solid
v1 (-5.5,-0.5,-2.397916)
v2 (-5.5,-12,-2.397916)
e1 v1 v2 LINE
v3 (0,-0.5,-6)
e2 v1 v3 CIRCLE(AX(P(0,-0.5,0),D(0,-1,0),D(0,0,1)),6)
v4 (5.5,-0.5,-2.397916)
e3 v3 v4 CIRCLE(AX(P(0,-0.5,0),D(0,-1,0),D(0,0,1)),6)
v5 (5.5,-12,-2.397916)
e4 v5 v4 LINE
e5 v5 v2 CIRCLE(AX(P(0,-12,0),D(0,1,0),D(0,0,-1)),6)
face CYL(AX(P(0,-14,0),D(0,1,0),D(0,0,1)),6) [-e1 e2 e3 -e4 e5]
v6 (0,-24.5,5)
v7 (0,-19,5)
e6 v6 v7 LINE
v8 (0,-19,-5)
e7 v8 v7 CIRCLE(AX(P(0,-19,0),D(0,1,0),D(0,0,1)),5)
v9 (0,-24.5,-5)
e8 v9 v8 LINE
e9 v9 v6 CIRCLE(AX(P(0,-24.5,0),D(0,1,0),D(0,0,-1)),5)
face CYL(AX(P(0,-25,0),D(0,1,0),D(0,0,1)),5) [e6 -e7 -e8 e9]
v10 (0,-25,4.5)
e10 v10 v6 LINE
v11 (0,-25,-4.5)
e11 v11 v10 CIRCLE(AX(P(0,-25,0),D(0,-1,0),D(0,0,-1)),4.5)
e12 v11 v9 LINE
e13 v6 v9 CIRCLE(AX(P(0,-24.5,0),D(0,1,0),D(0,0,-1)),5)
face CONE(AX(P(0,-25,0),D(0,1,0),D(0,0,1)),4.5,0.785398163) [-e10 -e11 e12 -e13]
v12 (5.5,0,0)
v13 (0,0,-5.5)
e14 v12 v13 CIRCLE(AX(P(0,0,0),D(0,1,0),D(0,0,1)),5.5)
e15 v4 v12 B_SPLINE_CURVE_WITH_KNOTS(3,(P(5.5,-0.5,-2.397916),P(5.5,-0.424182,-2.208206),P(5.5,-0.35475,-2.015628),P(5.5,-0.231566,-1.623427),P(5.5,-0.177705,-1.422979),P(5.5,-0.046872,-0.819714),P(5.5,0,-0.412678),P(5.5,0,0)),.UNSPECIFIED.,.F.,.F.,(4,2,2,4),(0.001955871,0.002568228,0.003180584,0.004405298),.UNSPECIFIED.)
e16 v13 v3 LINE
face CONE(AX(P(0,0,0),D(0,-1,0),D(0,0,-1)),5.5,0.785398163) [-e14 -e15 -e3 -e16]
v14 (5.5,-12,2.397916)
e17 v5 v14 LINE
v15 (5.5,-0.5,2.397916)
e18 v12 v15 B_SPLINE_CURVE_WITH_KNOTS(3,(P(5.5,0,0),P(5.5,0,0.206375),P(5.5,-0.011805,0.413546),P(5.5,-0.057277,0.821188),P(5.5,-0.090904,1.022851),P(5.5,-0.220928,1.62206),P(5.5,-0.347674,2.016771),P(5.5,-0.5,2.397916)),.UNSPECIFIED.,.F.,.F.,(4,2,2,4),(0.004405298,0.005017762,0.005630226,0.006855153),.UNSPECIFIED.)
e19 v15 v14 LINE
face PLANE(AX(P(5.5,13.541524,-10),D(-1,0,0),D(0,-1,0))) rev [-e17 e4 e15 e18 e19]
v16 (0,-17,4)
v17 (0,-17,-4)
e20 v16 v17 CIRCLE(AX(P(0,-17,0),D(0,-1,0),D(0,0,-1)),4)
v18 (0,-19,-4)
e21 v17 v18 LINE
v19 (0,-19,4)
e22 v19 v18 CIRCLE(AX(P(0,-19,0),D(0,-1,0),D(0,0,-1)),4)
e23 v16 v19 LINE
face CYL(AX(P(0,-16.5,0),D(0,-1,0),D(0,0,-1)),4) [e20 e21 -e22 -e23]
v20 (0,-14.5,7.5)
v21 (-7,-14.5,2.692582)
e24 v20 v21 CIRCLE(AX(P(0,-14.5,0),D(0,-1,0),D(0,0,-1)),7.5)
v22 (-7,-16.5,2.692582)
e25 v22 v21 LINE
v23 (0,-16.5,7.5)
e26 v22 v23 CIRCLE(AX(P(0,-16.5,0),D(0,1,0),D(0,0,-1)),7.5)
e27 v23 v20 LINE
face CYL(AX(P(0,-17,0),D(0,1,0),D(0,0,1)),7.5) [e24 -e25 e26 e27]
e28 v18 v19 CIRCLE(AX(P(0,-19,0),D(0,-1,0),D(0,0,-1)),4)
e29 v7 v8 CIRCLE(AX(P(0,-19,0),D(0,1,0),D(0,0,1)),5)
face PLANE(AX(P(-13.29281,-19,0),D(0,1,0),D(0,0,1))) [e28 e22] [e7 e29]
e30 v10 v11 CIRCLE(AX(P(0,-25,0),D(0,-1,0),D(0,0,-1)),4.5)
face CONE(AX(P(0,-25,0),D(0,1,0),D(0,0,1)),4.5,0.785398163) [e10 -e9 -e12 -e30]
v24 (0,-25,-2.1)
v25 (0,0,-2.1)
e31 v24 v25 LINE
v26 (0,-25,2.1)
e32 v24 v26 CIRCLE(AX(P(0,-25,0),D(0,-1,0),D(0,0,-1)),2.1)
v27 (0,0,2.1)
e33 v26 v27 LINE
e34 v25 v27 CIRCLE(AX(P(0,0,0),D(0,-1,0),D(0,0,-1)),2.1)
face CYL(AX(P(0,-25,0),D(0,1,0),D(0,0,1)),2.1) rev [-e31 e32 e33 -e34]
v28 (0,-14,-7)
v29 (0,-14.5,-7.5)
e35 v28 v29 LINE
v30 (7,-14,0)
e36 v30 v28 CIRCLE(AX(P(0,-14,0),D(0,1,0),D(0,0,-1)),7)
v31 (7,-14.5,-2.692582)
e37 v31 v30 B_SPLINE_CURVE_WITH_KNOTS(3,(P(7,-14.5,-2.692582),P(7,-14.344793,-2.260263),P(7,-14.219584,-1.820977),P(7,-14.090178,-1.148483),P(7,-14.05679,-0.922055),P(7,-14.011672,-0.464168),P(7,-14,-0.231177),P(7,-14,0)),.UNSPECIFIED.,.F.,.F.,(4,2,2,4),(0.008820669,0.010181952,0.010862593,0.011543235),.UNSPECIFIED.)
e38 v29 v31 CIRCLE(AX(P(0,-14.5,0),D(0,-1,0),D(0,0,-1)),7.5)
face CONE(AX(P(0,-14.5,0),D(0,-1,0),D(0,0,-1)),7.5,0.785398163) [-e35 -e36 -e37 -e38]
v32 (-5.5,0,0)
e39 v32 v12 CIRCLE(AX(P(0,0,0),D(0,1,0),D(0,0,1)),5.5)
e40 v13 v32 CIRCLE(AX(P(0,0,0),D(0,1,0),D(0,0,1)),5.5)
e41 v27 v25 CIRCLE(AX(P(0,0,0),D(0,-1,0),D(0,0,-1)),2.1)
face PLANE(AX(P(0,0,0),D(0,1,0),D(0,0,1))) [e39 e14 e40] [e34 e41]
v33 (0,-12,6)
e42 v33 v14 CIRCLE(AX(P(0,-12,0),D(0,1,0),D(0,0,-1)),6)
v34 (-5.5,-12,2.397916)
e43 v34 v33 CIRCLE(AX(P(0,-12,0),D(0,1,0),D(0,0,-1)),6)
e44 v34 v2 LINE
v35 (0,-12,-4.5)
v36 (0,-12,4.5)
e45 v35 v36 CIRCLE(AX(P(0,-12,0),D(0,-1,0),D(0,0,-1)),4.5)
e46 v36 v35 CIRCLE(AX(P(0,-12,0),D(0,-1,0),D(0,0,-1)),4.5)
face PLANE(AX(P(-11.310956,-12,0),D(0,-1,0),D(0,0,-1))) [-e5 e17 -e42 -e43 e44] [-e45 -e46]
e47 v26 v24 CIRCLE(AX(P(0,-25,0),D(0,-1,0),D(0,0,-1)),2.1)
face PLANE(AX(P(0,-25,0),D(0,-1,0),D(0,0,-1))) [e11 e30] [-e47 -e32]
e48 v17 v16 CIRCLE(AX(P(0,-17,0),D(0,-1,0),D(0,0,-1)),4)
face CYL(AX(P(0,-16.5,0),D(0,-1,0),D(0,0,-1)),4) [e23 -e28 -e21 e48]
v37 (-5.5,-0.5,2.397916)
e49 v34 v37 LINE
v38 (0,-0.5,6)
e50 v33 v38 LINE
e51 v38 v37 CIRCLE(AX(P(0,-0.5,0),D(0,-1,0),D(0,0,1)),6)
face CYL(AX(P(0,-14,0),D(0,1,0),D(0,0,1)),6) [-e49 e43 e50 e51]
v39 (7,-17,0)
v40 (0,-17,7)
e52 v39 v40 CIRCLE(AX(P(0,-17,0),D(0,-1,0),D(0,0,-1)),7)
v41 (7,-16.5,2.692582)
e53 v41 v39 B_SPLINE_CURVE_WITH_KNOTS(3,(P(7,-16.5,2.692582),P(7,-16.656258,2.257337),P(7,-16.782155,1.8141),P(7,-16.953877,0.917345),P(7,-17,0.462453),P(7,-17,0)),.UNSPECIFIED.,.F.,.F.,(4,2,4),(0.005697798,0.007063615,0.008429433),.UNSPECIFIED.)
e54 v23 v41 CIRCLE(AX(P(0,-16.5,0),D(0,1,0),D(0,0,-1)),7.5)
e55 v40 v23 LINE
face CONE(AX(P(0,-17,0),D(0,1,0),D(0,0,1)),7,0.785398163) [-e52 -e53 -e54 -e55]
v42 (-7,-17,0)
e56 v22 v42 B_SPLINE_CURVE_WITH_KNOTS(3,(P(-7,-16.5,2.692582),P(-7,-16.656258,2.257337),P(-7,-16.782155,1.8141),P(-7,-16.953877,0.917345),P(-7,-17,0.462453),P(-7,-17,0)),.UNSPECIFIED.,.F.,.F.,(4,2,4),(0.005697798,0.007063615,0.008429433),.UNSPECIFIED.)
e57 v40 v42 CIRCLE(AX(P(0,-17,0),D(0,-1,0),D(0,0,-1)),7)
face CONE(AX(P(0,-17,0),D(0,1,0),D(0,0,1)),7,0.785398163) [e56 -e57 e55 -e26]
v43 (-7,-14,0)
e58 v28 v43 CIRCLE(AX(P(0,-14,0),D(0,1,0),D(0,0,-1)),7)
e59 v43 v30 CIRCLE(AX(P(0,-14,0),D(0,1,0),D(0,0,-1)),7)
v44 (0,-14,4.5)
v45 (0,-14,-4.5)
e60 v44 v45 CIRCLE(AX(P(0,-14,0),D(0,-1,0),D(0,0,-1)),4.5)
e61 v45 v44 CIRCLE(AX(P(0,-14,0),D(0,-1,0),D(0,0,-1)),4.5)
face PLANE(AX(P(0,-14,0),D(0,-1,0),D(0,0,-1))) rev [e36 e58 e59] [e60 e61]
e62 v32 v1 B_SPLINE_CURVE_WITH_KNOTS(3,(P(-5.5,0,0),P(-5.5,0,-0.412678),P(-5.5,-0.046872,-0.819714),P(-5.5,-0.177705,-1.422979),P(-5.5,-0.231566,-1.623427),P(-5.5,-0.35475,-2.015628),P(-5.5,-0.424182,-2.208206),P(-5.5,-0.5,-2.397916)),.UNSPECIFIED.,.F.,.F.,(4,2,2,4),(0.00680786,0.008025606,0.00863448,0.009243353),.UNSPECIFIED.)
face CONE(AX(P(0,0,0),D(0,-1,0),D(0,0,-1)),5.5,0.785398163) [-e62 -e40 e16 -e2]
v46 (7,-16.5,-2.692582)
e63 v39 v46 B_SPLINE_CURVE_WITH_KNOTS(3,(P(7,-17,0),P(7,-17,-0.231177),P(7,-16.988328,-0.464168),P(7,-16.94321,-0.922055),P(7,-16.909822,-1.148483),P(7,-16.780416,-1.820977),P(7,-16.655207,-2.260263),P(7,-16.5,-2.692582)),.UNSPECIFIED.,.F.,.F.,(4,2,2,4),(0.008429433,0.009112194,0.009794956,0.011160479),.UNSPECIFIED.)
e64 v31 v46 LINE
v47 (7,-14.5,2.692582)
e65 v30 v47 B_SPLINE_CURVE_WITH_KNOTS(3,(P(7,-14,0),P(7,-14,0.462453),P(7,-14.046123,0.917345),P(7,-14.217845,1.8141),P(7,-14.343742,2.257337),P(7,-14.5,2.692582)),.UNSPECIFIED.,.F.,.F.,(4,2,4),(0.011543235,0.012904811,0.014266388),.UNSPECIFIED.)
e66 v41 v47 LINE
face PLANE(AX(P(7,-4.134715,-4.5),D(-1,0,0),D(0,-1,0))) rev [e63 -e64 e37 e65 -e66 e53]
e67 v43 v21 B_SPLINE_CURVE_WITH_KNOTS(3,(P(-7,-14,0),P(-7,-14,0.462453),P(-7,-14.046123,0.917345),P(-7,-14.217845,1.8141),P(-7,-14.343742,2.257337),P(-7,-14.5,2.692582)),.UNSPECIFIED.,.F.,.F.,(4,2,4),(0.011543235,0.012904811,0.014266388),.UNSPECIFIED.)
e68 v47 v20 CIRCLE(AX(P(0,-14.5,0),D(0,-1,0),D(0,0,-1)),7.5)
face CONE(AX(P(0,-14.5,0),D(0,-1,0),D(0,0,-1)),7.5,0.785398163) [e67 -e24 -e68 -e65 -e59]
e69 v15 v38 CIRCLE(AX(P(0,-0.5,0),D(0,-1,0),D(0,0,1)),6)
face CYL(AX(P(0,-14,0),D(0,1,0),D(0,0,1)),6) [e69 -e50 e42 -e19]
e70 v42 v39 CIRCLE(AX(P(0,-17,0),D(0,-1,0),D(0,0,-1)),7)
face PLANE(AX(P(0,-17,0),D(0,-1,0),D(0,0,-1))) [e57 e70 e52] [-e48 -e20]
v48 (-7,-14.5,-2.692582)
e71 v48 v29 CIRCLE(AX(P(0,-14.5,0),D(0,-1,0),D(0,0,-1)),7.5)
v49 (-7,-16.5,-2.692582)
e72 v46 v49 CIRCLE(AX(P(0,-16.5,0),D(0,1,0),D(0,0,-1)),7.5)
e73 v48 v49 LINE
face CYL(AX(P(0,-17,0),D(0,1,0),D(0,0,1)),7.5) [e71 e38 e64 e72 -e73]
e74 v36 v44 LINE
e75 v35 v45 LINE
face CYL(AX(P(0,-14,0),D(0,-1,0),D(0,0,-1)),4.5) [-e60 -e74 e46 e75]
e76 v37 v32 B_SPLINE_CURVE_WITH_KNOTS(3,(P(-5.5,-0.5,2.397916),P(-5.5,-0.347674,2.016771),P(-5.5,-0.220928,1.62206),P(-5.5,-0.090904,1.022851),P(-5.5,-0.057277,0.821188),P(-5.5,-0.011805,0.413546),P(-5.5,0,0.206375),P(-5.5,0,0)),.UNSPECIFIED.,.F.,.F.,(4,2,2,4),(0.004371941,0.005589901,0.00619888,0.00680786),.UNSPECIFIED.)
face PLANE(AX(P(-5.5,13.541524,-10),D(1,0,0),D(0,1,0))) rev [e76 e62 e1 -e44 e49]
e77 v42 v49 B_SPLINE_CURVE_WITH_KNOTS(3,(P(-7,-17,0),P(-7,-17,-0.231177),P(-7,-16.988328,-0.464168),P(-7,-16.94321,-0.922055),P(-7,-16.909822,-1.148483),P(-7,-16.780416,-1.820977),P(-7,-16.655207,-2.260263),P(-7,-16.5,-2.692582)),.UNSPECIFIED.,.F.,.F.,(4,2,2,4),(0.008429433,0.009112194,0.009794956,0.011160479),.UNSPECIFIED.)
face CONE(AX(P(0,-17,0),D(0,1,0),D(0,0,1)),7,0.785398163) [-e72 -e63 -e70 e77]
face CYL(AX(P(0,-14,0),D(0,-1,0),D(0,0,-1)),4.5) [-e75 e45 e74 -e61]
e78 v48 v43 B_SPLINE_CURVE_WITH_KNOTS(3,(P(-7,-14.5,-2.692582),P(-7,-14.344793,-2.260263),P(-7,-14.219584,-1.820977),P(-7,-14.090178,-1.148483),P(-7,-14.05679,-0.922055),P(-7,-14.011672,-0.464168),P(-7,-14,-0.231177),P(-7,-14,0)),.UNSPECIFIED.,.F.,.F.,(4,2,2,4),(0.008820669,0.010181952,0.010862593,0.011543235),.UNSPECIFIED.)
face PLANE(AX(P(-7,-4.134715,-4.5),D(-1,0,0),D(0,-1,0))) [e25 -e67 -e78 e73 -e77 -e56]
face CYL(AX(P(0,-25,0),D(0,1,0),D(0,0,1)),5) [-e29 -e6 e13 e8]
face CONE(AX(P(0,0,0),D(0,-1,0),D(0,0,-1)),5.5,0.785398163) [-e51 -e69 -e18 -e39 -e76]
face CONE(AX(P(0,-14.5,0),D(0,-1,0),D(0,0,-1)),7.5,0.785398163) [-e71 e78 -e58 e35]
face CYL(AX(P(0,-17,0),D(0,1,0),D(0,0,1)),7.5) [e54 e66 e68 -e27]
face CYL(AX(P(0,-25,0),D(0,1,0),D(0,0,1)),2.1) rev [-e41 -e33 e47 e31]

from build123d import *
from build123d.topology import SkipClean

# Parameters (mm, degrees)
SKETCH_1_R          = 6
EXTRUDE_1_DEPTH     = 14
SKETCH_2_R          = 7.5
EXTRUDE_2_DEPTH     = 3
SKETCH_3_R          = 5
EXTRUDE_3_DEPTH     = 8
SKETCH_8_R          = 2.1
CUT_EXTRUDE_1_DEPTH = 28.156951228
CHAMFER_1_SIZE      = 0.5
SKETCH_9_W          = 14.77232069
SKETCH_9_H          = 13.551998546
CUT_EXTRUDE_2_DEPTH = 4.5
CHAMFER_2_SIZE      = 0.5
SKETCH_11_W         = 9.643873146
SKETCH_11_H         = 27.541523797
SKETCH_11_W_2       = 13.856983611
CUT_EXTRUDE_3_DEPTH = 10
SKETCH_12_W         = 9.292809808
SKETCH_12_H         = 2
SKETCH_13_W         = 6.810956272
SKETCH_13_H         = 2


with BuildPart() as part:
    # 草图1 → 凸台-拉伸1 (new body)
    with BuildSketch(Plane(origin=(0, 0, 0), x_dir=(1, 0, 0), z_dir=(0, 1, 0))):
        with Locations(Location((0, 0, 0), (0, 0, 270))):
            Circle(SKETCH_1_R)
    extrude(amount=-EXTRUDE_1_DEPTH)

    # 草图2 → 凸台-拉伸2 (add)
    with BuildSketch(Plane.XZ.offset(14)):
        with Locations(Location((0, 0, 0), (0, 0, 270))):
            Circle(SKETCH_2_R)
    extrude(amount=EXTRUDE_2_DEPTH)

    # 草图3 → 凸台-拉伸3 (add)
    with BuildSketch(Plane.XZ.offset(17)):
        with Locations(Location((0, 0, 0), (0, 0, 270))):
            Circle(SKETCH_3_R)
    extrude(amount=EXTRUDE_3_DEPTH)

    # 草图8 → 切除-拉伸1 (cut, through all)
    with BuildSketch(Plane.XZ):
        with Locations(Location((0, 0, 0), (0, 0, 270))):
            Circle(SKETCH_8_R)
    extrude(amount=CUT_EXTRUDE_1_DEPTH, mode=Mode.SUBTRACT)

    # 倒角1
    chamfer_1_edges = [part.edges().sort_by_distance(p)[0] for p in [
        (0, 0, -6),
        (0, -14, 7.5),
        (0, -17, 7.5),
    ]]
    chamfer(chamfer_1_edges, length=CHAMFER_1_SIZE)

    # 草图9 → 切除-拉伸2 (cut, symmetric)
    with SkipClean():  # the faces are left unmerged after this step: merging them gives an invalid solid
        with BuildSketch(Plane.XY):
            with Locations((14.386160345, -10.910714622)):
                Rectangle(SKETCH_9_W, SKETCH_9_H)
        cut_extrude_2 = extrude(amount=CUT_EXTRUDE_2_DEPTH, both=True, mode=Mode.SUBTRACT)

    # 镜向1: 切除-拉伸2 across plane
    add(cut_extrude_2.mirror(Plane(origin=(0, 0, 0), x_dir=(0, 0, 1), z_dir=(1, 0, 0))), mode=Mode.SUBTRACT)

    # 倒角2
    chamfer_2_edges = [part.edges().sort_by_distance(p)[0] for p in [
        (0, -25, 5),
    ]]
    chamfer(chamfer_2_edges, length=CHAMFER_2_SIZE)

    # 草图11 → 切除-拉伸3 (cut, symmetric)
    with BuildSketch(Plane.XY):
        with Locations((10.321936573, -0.229238102)):
            Rectangle(SKETCH_11_W, SKETCH_11_H)
        with Locations((-12.428491806, -0.229238102)):
            Rectangle(SKETCH_11_W_2, SKETCH_11_H)
    extrude(amount=CUT_EXTRUDE_3_DEPTH, both=True, mode=Mode.SUBTRACT)

    # 草图12 → 切除-旋转2 (revolve, cut)
    with BuildSketch(Plane.XY, mode=Mode.PRIVATE) as cut_revolve_2_sk:
        with Locations((-8.646404904, -18)):
            Rectangle(SKETCH_12_W, SKETCH_12_H)
    revolve(cut_revolve_2_sk.sketch.rotate(Axis((0, -17, 0), (0, 1, 0)), 90), axis=Axis((0, -17, 0), (0, 1, 0)), mode=Mode.SUBTRACT)

    # 草图13 → 切除-旋转3 (revolve, cut)
    with BuildSketch(Plane.XY, mode=Mode.PRIVATE) as cut_revolve_3_sk:
        with Locations((-7.905478136, -13)):
            Rectangle(SKETCH_13_W, SKETCH_13_H)
    revolve(cut_revolve_3_sk.sketch.rotate(Axis((0, -14, 0), (0, 1, 0)), 270), axis=Axis((0, -14, 0), (0, 1, 0)), mode=Mode.SUBTRACT)


solid = part.part
